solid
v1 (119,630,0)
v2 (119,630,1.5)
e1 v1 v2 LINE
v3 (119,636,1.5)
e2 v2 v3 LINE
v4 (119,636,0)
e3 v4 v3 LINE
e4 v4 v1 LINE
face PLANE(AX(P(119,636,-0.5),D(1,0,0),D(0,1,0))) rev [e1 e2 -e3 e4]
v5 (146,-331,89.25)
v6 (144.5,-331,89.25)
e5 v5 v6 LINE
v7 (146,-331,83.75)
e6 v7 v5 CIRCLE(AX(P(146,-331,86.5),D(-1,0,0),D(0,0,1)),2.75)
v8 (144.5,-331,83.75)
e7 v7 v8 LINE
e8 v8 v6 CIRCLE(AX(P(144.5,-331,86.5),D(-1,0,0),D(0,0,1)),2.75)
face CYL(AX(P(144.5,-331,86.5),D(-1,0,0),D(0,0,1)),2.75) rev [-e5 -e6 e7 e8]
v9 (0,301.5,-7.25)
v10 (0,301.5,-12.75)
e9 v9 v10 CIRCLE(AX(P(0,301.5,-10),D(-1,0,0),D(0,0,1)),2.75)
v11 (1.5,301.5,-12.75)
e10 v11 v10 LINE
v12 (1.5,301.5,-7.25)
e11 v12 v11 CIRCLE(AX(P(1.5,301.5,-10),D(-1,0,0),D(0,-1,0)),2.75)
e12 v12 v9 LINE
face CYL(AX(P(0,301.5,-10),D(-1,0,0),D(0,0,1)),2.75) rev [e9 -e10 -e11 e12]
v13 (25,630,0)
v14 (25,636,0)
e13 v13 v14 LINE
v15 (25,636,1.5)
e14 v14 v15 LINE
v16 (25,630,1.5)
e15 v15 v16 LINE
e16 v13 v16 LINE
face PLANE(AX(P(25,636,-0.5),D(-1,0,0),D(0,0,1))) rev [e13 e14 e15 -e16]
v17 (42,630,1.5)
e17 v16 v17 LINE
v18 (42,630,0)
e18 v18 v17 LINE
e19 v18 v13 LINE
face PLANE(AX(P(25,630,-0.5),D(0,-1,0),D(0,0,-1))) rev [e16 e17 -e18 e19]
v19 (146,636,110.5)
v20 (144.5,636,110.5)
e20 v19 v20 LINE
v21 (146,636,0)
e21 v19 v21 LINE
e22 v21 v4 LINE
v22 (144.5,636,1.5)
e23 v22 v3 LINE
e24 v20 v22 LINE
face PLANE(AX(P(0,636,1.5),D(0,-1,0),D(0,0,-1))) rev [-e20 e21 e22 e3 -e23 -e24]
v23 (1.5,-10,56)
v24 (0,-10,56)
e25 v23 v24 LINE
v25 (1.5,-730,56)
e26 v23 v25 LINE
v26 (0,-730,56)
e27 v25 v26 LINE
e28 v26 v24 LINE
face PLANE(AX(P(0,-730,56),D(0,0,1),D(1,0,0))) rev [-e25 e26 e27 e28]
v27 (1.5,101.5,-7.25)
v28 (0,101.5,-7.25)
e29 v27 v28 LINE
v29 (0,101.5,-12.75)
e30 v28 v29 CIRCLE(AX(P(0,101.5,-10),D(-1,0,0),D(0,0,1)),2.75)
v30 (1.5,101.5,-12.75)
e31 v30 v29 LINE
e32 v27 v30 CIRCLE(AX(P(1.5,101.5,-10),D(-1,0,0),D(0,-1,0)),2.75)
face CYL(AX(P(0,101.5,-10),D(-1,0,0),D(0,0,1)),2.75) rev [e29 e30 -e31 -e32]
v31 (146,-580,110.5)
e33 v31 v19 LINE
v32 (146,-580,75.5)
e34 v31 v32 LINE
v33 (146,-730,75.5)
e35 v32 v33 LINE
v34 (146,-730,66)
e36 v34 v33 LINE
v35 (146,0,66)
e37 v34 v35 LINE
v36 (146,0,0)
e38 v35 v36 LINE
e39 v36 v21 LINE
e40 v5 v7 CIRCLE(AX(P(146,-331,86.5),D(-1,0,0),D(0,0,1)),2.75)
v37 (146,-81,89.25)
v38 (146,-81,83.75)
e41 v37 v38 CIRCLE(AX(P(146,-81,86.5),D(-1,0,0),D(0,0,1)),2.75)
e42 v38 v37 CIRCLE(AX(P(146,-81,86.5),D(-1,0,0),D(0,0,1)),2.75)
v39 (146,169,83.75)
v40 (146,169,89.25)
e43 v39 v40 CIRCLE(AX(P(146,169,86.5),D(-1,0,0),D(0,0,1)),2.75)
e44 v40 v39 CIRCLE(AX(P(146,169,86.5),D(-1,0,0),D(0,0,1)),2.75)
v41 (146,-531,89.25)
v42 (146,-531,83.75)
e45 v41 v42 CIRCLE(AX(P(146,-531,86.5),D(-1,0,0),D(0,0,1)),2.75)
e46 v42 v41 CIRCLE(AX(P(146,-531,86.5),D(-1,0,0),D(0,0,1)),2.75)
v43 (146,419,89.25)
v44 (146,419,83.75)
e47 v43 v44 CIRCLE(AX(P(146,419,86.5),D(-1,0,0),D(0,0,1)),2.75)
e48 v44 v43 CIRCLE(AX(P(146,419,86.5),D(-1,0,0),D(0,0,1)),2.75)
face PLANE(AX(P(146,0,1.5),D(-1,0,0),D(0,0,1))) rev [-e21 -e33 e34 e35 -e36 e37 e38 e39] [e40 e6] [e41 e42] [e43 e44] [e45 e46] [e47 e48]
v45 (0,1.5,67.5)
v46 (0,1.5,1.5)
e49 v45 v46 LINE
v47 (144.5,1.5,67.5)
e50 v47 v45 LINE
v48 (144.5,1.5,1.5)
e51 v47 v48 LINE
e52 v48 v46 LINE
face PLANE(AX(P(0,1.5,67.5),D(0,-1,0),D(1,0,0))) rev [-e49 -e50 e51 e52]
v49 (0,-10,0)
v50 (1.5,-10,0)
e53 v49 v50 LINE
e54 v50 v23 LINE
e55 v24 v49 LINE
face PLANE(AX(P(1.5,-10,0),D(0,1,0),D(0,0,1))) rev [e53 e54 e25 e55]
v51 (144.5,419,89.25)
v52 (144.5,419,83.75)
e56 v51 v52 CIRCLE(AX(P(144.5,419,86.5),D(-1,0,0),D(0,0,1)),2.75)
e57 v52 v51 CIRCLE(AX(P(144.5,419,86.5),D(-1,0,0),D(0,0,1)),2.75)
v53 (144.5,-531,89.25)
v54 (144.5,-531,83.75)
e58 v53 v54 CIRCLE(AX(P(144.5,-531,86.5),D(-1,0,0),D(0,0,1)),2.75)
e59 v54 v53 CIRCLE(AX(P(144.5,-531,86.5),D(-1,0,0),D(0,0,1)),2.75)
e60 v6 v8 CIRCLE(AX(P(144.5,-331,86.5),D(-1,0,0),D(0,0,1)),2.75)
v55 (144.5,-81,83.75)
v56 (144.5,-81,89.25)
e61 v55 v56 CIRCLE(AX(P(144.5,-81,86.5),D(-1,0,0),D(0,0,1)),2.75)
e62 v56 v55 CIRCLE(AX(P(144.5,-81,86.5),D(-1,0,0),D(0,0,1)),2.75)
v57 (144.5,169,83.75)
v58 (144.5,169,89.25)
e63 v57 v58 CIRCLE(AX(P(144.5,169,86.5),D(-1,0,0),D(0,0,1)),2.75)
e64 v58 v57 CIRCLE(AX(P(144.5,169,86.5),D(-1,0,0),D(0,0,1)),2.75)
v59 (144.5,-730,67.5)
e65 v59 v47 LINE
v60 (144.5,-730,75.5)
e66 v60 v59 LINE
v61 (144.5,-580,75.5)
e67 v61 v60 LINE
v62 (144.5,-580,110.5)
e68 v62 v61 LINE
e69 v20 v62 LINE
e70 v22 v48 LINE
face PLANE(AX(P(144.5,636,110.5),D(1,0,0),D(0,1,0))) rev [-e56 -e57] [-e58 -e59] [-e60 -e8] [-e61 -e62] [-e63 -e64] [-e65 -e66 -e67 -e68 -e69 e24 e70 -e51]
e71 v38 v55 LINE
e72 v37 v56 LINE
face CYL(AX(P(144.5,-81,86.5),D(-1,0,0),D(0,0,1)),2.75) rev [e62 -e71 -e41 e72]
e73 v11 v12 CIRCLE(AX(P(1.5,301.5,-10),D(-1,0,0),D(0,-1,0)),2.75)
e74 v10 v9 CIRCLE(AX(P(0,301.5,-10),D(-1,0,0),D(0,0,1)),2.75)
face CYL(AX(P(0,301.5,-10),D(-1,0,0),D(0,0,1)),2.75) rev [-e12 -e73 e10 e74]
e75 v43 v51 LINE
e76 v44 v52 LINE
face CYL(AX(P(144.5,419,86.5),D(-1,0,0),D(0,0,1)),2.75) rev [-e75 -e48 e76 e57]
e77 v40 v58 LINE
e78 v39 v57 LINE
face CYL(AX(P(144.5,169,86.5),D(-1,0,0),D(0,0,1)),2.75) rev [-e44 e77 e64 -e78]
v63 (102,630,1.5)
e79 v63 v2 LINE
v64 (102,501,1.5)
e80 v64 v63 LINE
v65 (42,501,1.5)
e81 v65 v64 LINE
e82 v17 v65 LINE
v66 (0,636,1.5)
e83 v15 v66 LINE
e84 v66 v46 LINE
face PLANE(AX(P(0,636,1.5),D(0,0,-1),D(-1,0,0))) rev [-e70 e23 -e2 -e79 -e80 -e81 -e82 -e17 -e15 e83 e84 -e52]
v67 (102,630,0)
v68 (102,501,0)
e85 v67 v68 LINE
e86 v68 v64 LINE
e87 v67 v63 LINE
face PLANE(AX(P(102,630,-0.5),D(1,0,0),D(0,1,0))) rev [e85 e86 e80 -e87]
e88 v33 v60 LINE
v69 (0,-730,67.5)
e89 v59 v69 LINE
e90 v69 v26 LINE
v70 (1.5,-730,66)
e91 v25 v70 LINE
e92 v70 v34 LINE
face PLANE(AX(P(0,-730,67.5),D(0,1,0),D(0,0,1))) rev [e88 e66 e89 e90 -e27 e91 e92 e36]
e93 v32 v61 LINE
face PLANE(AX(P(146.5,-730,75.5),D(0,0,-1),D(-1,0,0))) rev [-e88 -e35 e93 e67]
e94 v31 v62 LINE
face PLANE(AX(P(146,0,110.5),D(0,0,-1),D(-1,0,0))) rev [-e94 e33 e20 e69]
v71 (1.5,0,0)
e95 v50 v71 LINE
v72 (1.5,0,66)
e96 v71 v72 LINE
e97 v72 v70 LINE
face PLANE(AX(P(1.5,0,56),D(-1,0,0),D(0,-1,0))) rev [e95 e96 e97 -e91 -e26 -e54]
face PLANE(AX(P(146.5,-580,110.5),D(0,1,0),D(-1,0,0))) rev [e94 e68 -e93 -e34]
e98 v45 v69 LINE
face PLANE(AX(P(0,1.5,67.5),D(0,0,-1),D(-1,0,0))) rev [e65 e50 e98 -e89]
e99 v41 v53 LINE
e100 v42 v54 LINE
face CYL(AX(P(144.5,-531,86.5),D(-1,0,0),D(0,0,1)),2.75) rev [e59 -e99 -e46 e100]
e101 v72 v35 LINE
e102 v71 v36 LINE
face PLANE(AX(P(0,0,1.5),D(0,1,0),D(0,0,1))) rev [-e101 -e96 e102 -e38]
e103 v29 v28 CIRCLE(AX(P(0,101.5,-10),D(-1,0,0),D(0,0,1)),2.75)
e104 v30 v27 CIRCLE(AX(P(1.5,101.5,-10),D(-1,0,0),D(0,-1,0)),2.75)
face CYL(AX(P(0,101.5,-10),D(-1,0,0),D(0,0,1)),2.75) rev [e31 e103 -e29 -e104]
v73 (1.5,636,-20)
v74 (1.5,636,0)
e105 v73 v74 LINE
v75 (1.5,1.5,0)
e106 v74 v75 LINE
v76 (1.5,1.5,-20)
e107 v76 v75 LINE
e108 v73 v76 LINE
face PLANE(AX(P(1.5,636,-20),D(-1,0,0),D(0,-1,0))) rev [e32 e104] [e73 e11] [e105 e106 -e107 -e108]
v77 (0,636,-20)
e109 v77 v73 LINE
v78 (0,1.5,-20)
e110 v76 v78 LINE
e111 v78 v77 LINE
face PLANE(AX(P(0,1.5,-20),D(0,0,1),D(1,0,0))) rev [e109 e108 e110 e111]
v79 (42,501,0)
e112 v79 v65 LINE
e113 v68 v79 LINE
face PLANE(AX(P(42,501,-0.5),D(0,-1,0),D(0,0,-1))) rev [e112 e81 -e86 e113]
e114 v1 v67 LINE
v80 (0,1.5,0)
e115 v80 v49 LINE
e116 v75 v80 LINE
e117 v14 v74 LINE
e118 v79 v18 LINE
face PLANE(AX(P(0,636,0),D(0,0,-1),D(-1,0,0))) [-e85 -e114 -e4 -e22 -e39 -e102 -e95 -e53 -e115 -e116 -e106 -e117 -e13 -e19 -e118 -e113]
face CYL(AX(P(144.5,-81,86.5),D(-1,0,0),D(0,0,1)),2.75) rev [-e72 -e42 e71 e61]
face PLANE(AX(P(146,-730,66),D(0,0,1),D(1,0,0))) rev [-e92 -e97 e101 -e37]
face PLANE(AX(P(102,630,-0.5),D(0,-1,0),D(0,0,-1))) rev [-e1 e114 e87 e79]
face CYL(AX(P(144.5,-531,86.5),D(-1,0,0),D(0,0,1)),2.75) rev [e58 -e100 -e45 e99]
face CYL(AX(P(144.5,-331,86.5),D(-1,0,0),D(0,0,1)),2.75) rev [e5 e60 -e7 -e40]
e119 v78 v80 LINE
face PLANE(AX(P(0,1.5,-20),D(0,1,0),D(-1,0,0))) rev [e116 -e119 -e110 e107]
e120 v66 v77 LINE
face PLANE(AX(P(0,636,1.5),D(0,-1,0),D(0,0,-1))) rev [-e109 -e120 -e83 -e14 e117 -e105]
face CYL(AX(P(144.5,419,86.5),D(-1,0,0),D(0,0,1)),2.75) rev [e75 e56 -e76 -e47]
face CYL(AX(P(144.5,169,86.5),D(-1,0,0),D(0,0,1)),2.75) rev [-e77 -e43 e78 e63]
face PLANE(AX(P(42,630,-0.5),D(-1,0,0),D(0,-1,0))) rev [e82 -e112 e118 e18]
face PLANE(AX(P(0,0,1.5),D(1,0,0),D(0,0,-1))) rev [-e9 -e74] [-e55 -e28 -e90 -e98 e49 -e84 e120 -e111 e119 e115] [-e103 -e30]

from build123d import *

# Parameters (mm, degrees)
SKETCH_1_W              = 146
SKETCH_1_H              = 636
EXTRUDE_1_DEPTH         = 1.5
SKETCH_3_W              = 1.5
SKETCH_3_H              = 636
EXTRUDE_3_DEPTH         = 109
SKETCH_4_W              = 144.5
SKETCH_4_H              = 1.5
EXTRUDE_4_DEPTH         = 66
EXTRUDE_5_DEPTH         = 730
SKETCH_6_W              = 1.5
SKETCH_6_H              = 634.5
EXTRUDE_6_DEPTH         = 20
SKETCH_7_W              = 1.5
SKETCH_7_H              = 730
EXTRUDE_7_DEPTH         = 10
SKETCH_8_W              = 1.5
SKETCH_8_H              = 56
EXTRUDE_8_DEPTH         = 10
SKETCH_9_W              = 35
SKETCH_9_H              = 150
CUT_EXTRUDE_1_DEPTH     = 2
CUT_EXTRUDE_2_DEPTH     = 2
HOLE_WIZARD_5_5_5_5_1_D = 5.5
HOLE_WIZARD_5_5_5_5_2_D = 5.5


with BuildPart() as part:
    # 草图1 → 凸台-拉伸1 (new body)
    with BuildSketch(Plane.XY):
        with Locations((73, 318)):
            Rectangle(SKETCH_1_W, SKETCH_1_H)
    extrude(amount=EXTRUDE_1_DEPTH)

    # 草图3 → 凸台-拉伸3 (add)
    with BuildSketch(Plane.XY.offset(1.5)):
        with Locations((145.25, 318)):
            Rectangle(SKETCH_3_W, SKETCH_3_H)
    extrude(amount=EXTRUDE_3_DEPTH)

    # 草图4 → 凸台-拉伸4 (add)
    with BuildSketch(Plane.XY.offset(1.5)):
        with Locations((72.25, 0.75)):
            Rectangle(SKETCH_4_W, SKETCH_4_H)
    extrude(amount=EXTRUDE_4_DEPTH)

    # 草图5 → 凸台-拉伸5 (add)
    with BuildSketch(Plane.XZ):
        Polygon((0, 67.5), (144.5, 67.5), (144.5, 110.5), (146, 110.5), (146, 66), (0, 66), align=None)
    extrude(amount=EXTRUDE_5_DEPTH)

    # 草图6 → 凸台-拉伸6 (add)
    with BuildSketch(Plane(origin=(0, 0, 0), x_dir=(-1, 0, 0), z_dir=(0, 0, -1))):
        with Locations((-0.75, 318.75)):
            Rectangle(SKETCH_6_W, SKETCH_6_H)
    extrude(amount=EXTRUDE_6_DEPTH)

    # 草图7 → 凸台-拉伸7 (add)
    with BuildSketch(Plane(origin=(0, 0, 66), x_dir=(-1, 0, 0), z_dir=(0, 0, -1))):
        with Locations((-0.75, -365)):
            Rectangle(SKETCH_7_W, SKETCH_7_H)
    extrude(amount=EXTRUDE_7_DEPTH)

    # 草图8 → 凸台-拉伸8 (add)
    with BuildSketch(Plane.XZ):
        with Locations((0.75, 28)):
            Rectangle(SKETCH_8_W, SKETCH_8_H)
    extrude(amount=EXTRUDE_8_DEPTH)

    # 草图9 → 切除-拉伸1 (cut)
    with BuildSketch(Plane.ZY.offset(-144.5)):
        with Locations((93, -655)):
            Rectangle(SKETCH_9_W, SKETCH_9_H)
    extrude(amount=-CUT_EXTRUDE_1_DEPTH, mode=Mode.SUBTRACT)

    # 草图10 → 切除-拉伸2 (cut)
    with BuildSketch(Plane.XY.offset(1.5)):
        Polygon((25, 636), (119, 636), (119, 630), (102, 630), (102, 501), (42, 501), (42, 630), (25, 630), align=None)
    extrude(amount=-CUT_EXTRUDE_2_DEPTH, mode=Mode.SUBTRACT)

    # Ø5.5 (5.5) 直径孔1 (through all)
    with Locations(Plane.ZY.offset(-144.5)):
        with Locations((86.5, 419), (86.5, 169), (86.5, -81), (86.5, -331), (86.5, -531)):
            Hole(HOLE_WIZARD_5_5_5_5_1_D / 2)

    # Ø5.5 (5.5) 直径孔2 (through all)
    with Locations(Plane.ZY):
        with Locations((-10, 301.5), (-10, 101.5)):
            Hole(HOLE_WIZARD_5_5_5_5_2_D / 2)


solid = part.part
